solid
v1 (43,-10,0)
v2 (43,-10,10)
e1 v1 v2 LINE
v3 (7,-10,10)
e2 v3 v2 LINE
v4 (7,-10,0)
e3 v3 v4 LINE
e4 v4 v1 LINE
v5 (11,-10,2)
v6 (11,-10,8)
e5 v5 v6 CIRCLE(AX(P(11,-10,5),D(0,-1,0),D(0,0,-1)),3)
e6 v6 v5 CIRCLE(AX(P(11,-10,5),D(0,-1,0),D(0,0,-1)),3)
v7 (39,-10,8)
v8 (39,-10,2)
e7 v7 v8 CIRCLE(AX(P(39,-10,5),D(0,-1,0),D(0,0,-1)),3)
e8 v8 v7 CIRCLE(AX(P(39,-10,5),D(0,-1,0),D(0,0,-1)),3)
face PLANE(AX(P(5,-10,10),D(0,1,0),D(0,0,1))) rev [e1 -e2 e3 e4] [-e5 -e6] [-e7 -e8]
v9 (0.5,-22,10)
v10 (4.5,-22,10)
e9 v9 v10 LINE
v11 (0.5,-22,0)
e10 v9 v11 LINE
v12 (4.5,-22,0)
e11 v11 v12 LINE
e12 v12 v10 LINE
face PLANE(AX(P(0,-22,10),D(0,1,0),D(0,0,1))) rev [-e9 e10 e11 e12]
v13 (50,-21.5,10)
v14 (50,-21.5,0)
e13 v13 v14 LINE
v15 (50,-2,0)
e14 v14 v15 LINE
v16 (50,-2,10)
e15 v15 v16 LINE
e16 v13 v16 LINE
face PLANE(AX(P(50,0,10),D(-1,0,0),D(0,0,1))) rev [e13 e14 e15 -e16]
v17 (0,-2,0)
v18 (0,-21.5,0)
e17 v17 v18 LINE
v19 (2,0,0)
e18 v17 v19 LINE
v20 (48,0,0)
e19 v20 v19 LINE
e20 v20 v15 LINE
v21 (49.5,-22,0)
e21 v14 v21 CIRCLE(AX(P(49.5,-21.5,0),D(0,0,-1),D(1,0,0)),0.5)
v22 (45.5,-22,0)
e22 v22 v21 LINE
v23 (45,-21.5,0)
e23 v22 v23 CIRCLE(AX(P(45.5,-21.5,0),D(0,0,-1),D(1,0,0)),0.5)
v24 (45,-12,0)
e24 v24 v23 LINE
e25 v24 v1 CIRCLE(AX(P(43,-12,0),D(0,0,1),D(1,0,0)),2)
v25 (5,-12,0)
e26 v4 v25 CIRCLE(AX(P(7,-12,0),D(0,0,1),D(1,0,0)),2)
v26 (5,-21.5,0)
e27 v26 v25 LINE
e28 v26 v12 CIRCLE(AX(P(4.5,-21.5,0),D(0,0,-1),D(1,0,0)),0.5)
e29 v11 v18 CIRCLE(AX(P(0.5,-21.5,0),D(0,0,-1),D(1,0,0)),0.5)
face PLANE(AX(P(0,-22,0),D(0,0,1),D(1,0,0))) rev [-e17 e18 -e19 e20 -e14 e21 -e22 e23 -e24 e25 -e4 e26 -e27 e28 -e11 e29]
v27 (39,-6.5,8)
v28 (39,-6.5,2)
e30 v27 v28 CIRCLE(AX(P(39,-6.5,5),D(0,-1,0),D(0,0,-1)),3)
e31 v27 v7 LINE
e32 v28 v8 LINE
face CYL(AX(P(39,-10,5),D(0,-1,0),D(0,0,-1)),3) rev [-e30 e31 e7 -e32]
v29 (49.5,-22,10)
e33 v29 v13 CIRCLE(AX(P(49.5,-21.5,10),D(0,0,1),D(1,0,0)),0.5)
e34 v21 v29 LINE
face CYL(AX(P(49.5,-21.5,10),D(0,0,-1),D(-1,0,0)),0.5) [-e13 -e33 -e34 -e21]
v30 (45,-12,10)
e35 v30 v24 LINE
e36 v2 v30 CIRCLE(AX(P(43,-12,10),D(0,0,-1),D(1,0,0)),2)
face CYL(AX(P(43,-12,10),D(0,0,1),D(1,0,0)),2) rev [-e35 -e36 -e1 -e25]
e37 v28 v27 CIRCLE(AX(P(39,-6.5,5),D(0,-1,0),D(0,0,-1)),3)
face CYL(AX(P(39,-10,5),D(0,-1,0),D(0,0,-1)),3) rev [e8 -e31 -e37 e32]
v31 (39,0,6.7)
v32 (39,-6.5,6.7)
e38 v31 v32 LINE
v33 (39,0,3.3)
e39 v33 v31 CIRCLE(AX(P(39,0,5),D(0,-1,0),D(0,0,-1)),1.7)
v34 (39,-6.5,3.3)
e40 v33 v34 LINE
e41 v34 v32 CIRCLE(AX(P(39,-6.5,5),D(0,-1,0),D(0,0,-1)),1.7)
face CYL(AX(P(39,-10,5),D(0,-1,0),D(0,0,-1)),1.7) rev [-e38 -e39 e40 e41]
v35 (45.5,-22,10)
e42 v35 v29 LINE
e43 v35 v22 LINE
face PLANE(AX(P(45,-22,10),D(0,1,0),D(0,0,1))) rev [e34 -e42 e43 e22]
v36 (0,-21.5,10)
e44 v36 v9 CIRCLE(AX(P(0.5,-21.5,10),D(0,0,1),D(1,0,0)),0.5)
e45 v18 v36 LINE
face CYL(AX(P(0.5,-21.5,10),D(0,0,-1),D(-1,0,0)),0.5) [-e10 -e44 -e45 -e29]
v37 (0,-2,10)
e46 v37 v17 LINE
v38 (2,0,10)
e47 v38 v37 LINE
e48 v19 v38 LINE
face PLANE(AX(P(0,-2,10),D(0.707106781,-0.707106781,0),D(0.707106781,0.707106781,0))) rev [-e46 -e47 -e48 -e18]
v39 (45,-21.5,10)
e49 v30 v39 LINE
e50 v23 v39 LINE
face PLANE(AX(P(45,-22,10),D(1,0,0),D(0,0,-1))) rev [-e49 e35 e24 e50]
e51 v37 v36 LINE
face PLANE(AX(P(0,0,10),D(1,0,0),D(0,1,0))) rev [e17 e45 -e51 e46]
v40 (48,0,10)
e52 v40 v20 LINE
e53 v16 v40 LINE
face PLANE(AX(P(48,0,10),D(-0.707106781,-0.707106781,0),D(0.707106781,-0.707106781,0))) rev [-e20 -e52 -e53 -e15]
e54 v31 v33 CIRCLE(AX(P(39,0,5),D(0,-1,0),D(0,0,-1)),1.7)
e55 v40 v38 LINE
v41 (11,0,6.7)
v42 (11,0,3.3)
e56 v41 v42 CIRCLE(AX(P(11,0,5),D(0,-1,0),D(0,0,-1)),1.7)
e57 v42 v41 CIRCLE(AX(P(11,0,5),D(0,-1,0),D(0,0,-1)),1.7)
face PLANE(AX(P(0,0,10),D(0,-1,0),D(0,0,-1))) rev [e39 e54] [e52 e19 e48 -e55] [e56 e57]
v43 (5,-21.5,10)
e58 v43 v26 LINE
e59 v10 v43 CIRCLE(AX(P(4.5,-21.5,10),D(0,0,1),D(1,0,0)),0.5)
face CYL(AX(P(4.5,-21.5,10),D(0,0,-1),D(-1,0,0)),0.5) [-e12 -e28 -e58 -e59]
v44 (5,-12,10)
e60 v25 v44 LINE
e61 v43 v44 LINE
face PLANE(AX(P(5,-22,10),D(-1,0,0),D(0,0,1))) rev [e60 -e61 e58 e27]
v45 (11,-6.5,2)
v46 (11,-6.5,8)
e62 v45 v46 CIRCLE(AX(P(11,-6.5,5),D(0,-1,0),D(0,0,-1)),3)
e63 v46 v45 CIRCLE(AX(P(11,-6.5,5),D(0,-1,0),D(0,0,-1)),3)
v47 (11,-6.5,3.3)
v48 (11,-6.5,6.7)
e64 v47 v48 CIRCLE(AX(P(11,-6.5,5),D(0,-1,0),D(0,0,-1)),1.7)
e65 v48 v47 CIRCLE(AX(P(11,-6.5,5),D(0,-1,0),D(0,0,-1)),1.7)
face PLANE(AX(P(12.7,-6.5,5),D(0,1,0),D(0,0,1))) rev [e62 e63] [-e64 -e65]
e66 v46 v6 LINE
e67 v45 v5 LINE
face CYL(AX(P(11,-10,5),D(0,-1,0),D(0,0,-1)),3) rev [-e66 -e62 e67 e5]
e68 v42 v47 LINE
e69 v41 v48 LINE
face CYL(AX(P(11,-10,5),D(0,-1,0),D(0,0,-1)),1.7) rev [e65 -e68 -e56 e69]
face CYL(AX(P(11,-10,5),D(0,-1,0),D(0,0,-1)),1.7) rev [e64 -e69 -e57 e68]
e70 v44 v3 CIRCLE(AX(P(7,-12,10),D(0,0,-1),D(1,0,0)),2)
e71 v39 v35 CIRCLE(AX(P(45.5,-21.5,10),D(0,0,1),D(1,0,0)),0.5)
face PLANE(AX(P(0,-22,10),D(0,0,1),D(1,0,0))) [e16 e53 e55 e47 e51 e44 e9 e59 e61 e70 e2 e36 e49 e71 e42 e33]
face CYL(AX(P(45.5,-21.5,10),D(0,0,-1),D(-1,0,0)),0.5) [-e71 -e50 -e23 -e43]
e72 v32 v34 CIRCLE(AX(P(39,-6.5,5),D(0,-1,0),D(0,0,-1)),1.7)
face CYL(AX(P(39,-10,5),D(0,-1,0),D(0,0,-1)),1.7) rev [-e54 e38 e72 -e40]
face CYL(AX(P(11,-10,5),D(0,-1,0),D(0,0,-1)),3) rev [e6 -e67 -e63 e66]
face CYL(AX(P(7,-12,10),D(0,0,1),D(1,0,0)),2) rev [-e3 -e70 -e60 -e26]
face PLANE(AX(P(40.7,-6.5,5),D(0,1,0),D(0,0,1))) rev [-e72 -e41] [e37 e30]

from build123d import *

# Parameters (mm, degrees)
BOSS_EXTRUDE1_DEPTH                     = 10
CBORE_FOR_M3_HEX_HEAD_BOLT1_D           = 3.4
CBORE_FOR_M3_HEX_HEAD_BOLT1_CBORE_D     = 6
CBORE_FOR_M3_HEX_HEAD_BOLT1_CBORE_DEPTH = 3.5
FILLET1_R                               = 2
FILLET2_R                               = 0.5
CHAMFER1_SIZE                           = 2


with BuildPart() as part:
    # Sketch1 → Boss-Extrude1 (new body)
    with BuildSketch(Plane.XY):
        Polygon((45, -22), (50, -22), (50, 0), (0, 0), (0, -22), (5, -22), (5, -10), (45, -10), align=None)
    extrude(amount=BOSS_EXTRUDE1_DEPTH)

    # CBORE for M3 Hex Head Bolt1 (through all)
    with Locations(Plane.XZ.offset(10)):
        with Locations((11, 5), (39, 5)):
            CounterBoreHole(CBORE_FOR_M3_HEX_HEAD_BOLT1_D / 2, CBORE_FOR_M3_HEX_HEAD_BOLT1_CBORE_D / 2, CBORE_FOR_M3_HEX_HEAD_BOLT1_CBORE_DEPTH)

    # Fillet1
    fillet1_edges = [part.edges().sort_by_distance(p)[0] for p in [
        (45, -10, 5),
        (5, -10, 5),
    ]]
    fillet(fillet1_edges, radius=FILLET1_R)

    # Fillet2
    fillet2_edges = [part.edges().sort_by_distance(p)[0] for p in [
        (50, -22, 5),
        (45, -22, 5),
        (5, -22, 5),
        (0, -22, 5),
    ]]
    fillet(fillet2_edges, radius=FILLET2_R)

    # Chamfer1
    chamfer1_edges = [part.edges().sort_by_distance(p)[0] for p in [
        (0, 0, 5),
        (50, 0, 5),
    ]]
    chamfer(chamfer1_edges, length=CHAMFER1_SIZE)


solid = part.part
